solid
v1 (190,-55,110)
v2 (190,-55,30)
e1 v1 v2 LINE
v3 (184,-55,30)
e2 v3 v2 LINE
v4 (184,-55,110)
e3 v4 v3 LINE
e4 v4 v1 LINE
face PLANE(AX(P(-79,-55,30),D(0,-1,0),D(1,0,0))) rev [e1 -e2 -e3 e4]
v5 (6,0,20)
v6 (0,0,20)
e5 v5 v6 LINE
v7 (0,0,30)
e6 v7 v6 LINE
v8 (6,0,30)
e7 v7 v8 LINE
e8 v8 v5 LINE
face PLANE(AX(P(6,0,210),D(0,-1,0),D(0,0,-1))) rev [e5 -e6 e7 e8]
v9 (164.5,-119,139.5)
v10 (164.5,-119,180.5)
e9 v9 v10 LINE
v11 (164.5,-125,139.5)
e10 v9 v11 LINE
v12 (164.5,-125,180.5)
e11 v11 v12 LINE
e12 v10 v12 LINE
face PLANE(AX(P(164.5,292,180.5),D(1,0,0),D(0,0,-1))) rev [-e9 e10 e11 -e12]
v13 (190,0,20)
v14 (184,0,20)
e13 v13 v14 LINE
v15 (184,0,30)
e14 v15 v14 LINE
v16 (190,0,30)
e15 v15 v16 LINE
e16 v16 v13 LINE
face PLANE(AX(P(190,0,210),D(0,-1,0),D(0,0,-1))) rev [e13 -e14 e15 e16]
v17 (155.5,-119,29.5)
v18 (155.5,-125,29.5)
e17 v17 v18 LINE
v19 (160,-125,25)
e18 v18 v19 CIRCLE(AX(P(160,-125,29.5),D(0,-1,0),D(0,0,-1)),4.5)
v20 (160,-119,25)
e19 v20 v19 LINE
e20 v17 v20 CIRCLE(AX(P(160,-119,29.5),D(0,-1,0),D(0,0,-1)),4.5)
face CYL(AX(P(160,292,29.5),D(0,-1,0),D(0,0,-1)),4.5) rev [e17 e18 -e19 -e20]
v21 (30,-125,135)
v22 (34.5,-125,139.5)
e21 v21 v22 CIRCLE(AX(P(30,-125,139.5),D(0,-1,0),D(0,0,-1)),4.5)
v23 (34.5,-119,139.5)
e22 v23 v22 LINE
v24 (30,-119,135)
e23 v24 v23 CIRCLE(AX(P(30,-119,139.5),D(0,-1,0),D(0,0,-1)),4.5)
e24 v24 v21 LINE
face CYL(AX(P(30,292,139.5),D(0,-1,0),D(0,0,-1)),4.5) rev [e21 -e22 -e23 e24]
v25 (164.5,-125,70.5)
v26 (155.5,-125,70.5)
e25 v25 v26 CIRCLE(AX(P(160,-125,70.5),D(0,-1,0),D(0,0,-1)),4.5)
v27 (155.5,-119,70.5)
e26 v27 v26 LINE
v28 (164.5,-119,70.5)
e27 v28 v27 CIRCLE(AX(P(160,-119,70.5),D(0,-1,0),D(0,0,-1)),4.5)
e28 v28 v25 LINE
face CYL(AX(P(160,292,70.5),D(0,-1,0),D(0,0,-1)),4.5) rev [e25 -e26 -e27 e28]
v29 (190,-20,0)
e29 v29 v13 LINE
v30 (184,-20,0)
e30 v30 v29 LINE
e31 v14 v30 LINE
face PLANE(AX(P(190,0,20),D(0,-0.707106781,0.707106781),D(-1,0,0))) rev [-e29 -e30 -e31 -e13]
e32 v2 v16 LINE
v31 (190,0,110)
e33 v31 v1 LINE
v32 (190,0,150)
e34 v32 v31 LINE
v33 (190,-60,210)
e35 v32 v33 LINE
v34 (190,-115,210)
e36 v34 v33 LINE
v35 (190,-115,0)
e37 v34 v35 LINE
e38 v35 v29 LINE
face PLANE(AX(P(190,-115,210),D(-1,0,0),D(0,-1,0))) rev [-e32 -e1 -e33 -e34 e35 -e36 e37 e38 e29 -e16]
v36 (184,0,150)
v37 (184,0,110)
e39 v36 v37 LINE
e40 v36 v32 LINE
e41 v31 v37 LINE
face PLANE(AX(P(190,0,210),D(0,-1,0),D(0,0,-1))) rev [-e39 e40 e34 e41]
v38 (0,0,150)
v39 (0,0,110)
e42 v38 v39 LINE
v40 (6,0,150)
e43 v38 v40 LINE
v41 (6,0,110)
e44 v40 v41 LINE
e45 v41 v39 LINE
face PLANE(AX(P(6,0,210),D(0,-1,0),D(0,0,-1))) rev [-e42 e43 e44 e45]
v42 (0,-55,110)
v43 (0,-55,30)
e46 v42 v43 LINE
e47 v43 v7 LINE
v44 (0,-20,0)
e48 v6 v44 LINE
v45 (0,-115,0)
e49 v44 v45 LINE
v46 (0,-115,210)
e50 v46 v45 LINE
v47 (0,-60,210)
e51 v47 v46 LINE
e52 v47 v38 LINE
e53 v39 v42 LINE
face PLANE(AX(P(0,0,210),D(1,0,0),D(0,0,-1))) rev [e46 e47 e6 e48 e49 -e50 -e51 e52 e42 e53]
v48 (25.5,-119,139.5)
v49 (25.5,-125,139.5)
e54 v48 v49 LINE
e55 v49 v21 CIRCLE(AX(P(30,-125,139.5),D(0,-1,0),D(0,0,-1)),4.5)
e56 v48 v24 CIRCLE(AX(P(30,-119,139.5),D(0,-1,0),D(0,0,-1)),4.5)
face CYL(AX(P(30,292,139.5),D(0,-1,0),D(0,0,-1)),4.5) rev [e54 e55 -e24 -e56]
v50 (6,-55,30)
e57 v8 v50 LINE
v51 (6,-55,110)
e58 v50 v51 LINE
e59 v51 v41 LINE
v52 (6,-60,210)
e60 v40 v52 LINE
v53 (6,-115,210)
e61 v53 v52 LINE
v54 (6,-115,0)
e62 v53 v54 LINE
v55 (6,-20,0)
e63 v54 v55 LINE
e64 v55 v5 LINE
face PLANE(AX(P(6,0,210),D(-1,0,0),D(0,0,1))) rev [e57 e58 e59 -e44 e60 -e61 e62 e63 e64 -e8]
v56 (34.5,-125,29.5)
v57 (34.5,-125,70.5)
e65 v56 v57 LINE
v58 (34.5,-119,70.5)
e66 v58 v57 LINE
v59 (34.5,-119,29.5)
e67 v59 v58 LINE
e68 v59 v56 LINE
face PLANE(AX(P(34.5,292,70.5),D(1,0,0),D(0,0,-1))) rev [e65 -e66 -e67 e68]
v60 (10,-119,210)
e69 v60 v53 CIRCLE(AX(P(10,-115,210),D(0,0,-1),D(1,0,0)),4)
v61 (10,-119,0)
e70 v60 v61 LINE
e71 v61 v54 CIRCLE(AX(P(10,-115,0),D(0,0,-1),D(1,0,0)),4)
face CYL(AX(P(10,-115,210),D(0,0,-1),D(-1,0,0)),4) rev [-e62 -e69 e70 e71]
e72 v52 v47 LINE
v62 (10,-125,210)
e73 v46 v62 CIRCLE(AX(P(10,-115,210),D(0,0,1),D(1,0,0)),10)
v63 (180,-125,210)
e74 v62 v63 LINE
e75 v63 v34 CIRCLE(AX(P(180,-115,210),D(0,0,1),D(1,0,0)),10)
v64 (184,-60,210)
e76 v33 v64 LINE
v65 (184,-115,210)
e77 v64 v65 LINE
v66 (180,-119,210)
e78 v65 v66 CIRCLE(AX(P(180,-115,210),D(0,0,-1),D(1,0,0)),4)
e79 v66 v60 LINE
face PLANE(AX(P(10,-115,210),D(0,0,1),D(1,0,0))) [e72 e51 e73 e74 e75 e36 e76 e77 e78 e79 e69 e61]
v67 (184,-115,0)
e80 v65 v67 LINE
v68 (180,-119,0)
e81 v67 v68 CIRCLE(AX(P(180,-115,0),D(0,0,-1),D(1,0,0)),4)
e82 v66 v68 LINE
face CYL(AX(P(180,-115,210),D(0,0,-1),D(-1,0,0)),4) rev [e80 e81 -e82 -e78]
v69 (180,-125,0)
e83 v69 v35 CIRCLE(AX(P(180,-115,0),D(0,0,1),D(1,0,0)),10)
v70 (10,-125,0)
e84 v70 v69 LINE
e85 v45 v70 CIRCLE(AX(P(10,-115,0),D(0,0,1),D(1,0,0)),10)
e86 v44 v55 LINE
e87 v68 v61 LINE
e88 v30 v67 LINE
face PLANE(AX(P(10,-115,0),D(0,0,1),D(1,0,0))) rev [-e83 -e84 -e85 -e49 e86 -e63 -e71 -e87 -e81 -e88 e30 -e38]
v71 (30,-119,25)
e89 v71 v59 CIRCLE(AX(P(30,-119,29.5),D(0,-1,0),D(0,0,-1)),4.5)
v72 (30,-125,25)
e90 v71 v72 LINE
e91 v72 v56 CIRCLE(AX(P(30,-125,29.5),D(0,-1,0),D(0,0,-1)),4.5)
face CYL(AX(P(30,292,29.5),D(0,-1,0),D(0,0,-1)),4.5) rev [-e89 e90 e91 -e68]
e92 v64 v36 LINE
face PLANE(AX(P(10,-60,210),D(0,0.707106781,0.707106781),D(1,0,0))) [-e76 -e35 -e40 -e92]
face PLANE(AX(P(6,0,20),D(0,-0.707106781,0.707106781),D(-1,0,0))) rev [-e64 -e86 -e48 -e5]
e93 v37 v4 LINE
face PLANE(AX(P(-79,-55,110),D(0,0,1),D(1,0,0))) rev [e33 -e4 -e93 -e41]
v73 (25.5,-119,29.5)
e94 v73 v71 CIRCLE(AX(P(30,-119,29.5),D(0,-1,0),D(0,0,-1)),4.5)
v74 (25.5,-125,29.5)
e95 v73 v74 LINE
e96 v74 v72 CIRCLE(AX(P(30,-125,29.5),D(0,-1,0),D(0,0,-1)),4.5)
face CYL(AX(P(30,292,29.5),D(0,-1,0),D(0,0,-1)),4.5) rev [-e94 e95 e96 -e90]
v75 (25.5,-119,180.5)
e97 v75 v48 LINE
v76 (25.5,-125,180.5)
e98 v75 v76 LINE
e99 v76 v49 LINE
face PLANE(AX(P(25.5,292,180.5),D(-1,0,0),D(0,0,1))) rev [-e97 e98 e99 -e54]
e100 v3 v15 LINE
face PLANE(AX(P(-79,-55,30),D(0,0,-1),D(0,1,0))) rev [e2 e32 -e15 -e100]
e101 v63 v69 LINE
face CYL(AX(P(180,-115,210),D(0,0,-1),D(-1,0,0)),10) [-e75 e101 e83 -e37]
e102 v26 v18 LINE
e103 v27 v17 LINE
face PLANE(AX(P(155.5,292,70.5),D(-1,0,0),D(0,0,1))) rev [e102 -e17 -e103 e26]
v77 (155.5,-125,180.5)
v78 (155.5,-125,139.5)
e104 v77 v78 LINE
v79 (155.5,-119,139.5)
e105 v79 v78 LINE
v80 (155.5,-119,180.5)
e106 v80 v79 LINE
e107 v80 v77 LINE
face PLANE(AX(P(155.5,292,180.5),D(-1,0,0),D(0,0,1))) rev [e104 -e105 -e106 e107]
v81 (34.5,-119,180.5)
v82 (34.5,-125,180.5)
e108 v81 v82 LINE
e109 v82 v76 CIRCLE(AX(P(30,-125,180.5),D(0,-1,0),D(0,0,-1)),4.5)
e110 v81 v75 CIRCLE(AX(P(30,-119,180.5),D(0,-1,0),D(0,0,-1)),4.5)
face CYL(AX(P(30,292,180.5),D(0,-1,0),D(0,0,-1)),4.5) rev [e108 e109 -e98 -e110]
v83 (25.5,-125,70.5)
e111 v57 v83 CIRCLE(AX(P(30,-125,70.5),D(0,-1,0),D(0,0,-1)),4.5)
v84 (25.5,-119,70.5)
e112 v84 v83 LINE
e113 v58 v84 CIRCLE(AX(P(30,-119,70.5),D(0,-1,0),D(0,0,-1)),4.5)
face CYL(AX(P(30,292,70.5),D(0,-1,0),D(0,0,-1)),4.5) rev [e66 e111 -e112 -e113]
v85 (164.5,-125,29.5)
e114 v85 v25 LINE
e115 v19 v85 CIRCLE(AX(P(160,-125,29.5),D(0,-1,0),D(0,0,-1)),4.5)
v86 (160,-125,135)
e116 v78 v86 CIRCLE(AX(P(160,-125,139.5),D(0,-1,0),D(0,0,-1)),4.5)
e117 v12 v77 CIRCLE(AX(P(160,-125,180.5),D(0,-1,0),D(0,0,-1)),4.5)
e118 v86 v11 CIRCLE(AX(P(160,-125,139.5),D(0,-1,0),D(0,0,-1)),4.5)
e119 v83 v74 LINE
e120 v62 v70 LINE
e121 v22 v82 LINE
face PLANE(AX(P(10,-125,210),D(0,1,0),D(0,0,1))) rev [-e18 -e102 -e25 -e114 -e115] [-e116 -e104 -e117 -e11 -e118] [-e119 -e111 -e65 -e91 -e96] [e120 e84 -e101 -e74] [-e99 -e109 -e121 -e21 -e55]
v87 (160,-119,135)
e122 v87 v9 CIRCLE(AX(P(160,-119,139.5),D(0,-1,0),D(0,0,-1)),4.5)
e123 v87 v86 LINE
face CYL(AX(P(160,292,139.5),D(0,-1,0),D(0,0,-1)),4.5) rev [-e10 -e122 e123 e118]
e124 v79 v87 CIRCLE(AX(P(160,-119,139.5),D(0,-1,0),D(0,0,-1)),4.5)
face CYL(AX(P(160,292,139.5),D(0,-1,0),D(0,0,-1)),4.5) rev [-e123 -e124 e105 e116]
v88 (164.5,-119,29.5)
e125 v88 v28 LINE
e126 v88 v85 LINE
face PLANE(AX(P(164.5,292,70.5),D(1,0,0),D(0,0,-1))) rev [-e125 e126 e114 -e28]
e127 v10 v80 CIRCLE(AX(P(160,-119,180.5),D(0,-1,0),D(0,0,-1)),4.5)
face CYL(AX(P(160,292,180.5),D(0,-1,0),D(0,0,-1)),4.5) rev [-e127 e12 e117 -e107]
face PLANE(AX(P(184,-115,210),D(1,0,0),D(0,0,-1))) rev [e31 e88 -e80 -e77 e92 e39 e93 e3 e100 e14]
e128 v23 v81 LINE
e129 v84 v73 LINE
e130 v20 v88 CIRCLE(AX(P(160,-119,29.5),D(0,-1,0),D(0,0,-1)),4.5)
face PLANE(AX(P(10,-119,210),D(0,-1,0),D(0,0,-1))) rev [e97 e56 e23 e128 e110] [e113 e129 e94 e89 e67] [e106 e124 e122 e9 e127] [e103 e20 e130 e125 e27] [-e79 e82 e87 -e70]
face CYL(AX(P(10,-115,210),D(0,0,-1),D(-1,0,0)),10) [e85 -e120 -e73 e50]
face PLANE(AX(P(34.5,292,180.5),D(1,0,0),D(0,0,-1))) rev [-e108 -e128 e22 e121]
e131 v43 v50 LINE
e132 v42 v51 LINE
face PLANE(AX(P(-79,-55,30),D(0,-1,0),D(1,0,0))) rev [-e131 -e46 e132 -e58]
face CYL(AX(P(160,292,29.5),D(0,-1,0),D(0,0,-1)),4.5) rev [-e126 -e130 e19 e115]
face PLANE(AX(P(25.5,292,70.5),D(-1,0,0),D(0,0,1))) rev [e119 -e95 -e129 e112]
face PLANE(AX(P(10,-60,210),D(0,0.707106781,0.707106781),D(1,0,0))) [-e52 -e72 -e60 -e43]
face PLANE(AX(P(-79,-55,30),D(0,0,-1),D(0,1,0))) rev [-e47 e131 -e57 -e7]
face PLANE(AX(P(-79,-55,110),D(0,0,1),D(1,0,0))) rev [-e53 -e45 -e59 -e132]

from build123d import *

# Parameters (mm, degrees)
EXTRUDE_1_DEPTH     = 210
CHAMFER_1_SIZE      = 60
CHAMFER_2_SIZE      = 20
CUT_EXTRUDE_1_DEPTH = 417
SKETCH_4_W          = 80
SKETCH_4_H          = 90.775966299
CUT_EXTRUDE_2_DEPTH = 269


with BuildPart() as part:
    # 草图1 → 凸台-拉伸1 (new body)
    with BuildSketch(Plane.XY):
        with BuildLine():
            Line((0, 0), (0, -115))
            ThreePointArc((0, -115), (2.928932188, -122.071067812), (10, -125))
            Line((10, -125), (180, -125))
            ThreePointArc((180, -125), (187.071067812, -122.071067812), (190, -115))
            Line((190, -115), (190, 0))
            Line((190, 0), (184, 0))
            Line((184, 0), (184, -115))
            ThreePointArc((184, -115), (182.828427125, -117.828427125), (180, -119))
            Line((180, -119), (10, -119))
            ThreePointArc((10, -119), (7.171572875, -117.828427125), (6, -115))
            Line((6, -115), (6, 0))
            Line((6, 0), (0, 0))
        make_face()
    extrude(amount=EXTRUDE_1_DEPTH)

    # 倒角1
    chamfer_1_edges = [part.edges().sort_by_distance(p)[0] for p in [
        (187, 0, 210),
        (3, 0, 210),
    ]]
    chamfer(chamfer_1_edges, length=CHAMFER_1_SIZE)

    # 倒角2
    chamfer_2_edges = [part.edges().sort_by_distance(p)[0] for p in [
        (187, 0, 0),
        (3, 0, 0),
    ]]
    chamfer(chamfer_2_edges, length=CHAMFER_2_SIZE)

    # 草图3 → 切除-拉伸1 (cut)
    with BuildSketch(Plane.XZ.offset(125)):
        with BuildLine():
            Line((34.5, 180.5), (34.5, 139.5))
            ThreePointArc((34.5, 139.5), (30, 135), (25.5, 139.5))
            Line((25.5, 139.5), (25.5, 180.5))
            ThreePointArc((25.5, 180.5), (30, 185), (34.5, 180.5))
        make_face()
        with BuildLine():
            Line((164.5, 180.5), (164.5, 139.5))
            ThreePointArc((164.5, 139.5), (160, 135), (155.5, 139.5))
            Line((155.5, 139.5), (155.5, 180.5))
            ThreePointArc((155.5, 180.5), (160, 185), (164.5, 180.5))
        make_face()
        with BuildLine():
            Line((34.5, 70.5), (34.5, 29.5))
            ThreePointArc((34.5, 29.5), (30, 25), (25.5, 29.5))
            Line((25.5, 29.5), (25.5, 70.5))
            ThreePointArc((25.5, 70.5), (30, 75), (34.5, 70.5))
        make_face()
        with BuildLine():
            Line((164.5, 70.5), (164.5, 29.5))
            ThreePointArc((164.5, 29.5), (160, 25), (155.5, 29.5))
            Line((155.5, 29.5), (155.5, 70.5))
            ThreePointArc((155.5, 70.5), (160, 75), (164.5, 70.5))
        make_face()
    extrude(amount=-CUT_EXTRUDE_1_DEPTH, mode=Mode.SUBTRACT)

    # 草图4 → 切除-拉伸2 (cut)
    with BuildSketch(Plane(origin=(190, 0, 0), x_dir=(0, 0, -1), z_dir=(1, 0, 0))):
        with Locations((-70, -9.61201685)):
            Rectangle(SKETCH_4_W, SKETCH_4_H)
    extrude(amount=-CUT_EXTRUDE_2_DEPTH, mode=Mode.SUBTRACT)


solid = part.part
